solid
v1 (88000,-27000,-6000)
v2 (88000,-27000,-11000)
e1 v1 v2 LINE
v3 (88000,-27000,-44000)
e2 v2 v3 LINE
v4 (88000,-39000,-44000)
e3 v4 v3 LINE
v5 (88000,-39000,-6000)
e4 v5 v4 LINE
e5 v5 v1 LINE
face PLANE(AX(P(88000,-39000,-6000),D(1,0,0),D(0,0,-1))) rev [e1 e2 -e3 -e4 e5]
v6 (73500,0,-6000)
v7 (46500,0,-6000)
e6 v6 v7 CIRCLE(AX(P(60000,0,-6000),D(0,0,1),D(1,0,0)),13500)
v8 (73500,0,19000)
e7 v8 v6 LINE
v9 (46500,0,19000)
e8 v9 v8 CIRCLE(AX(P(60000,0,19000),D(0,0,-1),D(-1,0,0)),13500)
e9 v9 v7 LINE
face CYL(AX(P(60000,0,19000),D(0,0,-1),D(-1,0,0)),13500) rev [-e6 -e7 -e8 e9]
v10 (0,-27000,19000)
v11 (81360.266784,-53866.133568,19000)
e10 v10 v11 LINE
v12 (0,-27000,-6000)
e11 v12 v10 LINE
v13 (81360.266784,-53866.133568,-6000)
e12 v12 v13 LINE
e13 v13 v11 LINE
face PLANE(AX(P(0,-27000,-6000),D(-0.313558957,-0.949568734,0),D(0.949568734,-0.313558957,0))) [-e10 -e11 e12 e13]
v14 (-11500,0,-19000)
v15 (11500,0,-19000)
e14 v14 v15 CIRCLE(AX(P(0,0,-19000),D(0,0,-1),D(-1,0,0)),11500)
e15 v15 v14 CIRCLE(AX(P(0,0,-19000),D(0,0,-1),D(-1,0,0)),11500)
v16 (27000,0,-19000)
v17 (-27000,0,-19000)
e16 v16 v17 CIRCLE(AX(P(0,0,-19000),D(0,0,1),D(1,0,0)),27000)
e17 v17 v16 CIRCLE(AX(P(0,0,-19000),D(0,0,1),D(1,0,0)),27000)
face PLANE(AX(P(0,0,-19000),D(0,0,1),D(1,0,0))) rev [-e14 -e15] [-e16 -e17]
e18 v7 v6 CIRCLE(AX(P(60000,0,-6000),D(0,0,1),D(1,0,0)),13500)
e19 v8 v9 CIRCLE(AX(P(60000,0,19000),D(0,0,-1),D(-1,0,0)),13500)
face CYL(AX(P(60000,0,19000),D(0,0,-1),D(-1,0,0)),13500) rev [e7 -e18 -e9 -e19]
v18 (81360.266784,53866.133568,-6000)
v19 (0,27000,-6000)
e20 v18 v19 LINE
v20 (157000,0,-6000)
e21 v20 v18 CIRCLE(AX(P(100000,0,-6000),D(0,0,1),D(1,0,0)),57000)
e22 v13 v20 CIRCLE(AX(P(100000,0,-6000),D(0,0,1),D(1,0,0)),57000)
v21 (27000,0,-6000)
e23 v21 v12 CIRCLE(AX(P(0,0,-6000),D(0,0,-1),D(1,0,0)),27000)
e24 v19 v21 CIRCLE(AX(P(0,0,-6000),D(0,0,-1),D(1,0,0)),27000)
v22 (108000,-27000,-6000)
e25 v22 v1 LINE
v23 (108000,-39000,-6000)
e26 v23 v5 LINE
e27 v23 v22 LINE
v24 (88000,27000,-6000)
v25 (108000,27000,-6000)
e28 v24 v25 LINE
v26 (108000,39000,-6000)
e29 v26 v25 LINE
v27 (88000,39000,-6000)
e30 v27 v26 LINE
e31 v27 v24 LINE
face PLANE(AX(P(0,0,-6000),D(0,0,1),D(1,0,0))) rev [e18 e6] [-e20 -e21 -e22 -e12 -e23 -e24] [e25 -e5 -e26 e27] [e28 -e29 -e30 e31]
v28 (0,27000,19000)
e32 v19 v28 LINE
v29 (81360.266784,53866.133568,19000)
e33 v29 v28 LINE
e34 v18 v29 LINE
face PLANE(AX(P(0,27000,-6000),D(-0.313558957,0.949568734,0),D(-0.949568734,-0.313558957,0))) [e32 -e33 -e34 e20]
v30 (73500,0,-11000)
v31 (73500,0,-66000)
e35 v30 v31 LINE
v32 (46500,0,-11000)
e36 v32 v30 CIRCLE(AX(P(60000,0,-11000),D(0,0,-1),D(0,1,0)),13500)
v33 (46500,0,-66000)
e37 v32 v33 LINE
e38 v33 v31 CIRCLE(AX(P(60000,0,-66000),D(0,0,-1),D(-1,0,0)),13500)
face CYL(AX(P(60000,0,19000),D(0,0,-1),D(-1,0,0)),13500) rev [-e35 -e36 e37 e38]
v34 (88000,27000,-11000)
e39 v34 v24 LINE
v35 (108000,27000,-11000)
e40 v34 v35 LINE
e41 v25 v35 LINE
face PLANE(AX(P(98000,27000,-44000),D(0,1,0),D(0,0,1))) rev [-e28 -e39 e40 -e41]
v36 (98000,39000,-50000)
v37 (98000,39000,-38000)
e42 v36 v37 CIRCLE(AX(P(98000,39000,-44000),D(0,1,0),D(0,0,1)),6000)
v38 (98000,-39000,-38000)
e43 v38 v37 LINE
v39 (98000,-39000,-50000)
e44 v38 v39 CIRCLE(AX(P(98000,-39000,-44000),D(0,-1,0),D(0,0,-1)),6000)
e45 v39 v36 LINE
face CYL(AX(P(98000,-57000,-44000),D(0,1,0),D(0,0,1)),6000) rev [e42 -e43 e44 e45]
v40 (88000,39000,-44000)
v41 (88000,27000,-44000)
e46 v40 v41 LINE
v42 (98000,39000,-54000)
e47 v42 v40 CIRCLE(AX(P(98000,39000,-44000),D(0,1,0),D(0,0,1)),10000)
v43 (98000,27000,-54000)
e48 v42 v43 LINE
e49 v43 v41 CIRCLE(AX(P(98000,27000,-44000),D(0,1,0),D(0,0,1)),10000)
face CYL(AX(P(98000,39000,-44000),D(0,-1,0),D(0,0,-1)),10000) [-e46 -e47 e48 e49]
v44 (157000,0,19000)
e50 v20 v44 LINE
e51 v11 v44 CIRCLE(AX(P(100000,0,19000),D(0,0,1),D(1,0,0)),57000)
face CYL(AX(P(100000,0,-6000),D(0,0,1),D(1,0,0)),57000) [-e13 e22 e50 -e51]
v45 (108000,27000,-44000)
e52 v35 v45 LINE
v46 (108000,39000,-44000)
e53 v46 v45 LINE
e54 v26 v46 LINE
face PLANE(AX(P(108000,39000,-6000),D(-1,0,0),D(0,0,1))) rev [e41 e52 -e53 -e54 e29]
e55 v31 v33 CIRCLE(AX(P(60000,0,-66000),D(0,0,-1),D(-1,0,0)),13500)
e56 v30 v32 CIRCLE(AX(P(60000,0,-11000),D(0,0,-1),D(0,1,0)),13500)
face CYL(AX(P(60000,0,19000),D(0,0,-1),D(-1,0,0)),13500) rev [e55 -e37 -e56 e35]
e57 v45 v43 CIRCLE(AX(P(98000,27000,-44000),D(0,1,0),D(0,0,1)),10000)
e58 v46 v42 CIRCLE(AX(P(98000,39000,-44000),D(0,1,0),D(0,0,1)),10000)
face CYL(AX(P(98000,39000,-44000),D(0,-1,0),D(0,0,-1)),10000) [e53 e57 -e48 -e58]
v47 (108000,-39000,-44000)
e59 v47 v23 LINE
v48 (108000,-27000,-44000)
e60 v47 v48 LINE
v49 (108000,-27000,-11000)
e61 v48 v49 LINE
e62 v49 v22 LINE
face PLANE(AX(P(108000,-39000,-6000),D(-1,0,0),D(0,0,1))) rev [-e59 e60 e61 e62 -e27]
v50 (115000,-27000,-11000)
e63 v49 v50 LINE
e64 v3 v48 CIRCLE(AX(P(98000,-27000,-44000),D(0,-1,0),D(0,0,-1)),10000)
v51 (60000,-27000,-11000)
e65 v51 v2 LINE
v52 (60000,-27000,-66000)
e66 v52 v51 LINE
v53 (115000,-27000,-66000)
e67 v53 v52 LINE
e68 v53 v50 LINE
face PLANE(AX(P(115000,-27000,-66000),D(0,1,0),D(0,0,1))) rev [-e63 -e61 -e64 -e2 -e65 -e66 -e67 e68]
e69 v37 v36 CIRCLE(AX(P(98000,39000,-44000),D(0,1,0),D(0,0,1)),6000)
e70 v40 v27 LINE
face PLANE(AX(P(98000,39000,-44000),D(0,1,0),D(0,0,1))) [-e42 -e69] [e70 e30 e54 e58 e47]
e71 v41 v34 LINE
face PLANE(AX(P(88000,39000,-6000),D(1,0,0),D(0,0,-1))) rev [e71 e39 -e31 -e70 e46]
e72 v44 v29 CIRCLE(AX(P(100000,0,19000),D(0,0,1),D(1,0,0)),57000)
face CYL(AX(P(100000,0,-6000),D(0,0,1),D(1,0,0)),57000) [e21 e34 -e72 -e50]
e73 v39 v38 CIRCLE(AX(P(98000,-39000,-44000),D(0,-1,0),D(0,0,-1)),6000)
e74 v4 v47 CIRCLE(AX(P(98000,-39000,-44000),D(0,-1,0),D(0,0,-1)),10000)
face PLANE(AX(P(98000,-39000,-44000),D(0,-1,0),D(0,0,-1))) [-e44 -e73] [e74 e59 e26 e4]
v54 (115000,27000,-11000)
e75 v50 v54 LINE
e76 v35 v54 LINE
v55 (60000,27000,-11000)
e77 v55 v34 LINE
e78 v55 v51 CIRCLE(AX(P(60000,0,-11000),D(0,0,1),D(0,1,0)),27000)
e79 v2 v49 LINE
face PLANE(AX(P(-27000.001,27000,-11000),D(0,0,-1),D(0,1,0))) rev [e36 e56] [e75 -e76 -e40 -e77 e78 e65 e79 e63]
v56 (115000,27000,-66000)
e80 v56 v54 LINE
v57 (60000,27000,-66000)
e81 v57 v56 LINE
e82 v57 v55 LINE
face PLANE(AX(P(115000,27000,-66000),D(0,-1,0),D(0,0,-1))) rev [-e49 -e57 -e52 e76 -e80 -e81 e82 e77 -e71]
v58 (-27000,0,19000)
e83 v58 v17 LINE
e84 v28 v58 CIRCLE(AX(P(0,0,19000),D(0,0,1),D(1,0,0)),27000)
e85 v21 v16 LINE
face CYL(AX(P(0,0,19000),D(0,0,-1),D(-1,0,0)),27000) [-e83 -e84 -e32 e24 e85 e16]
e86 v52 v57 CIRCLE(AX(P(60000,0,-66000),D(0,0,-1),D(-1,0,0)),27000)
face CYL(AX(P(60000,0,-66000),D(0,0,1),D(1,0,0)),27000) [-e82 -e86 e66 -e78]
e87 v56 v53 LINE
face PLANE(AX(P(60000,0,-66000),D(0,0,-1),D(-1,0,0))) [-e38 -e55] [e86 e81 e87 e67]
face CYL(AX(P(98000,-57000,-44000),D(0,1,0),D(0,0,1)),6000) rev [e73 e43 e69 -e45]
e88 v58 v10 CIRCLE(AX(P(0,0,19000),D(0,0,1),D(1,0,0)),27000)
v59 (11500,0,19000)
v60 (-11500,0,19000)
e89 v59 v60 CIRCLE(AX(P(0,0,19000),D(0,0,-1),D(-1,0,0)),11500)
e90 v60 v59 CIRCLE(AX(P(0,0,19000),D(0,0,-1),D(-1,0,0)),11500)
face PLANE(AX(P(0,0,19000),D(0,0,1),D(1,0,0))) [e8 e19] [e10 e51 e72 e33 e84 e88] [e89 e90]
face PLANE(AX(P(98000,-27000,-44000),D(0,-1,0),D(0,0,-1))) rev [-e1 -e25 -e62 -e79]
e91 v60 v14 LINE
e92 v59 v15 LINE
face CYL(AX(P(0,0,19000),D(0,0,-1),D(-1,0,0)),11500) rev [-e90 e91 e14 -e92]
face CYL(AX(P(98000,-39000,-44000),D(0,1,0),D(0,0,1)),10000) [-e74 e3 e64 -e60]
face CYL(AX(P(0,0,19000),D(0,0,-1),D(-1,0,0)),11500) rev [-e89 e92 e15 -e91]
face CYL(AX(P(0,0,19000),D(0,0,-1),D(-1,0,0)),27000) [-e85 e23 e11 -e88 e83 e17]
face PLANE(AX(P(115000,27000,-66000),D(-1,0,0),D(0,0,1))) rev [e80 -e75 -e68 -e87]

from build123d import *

# Parameters (mm, degrees)
HUB_SKETCH_54_R      = 27000
HUB_BOSS_54_DEPTH    = 19000
BASE_PLATE_DEPTH     = 25000
MOUNTING_BLOCK_DEPTH = 60000
PLATE_HOLE_SKETCH_R  = 13500
PLATE_HOLE_DEPTH     = 187412.312358673
HUB_BORE_SKETCH_23_R = 11500
HUB_BORE_23_DEPTH    = 173514.688220843
BLOCK_SLOT_REACH     = 166642.331
BLOCK_SLOT_SKETCH_W  = 5000
BLOCK_SLOT_SKETCH_H  = 54000
CLEVIS_LUG_1_DEPTH   = 12000
CLEVIS_LUG_2_DEPTH   = 12000
PIN_HOLE_SKETCH_12_R = 6000
PIN_HOLE_12_DEPTH    = 195502.918149158


with BuildPart() as part:
    # Hub Sketch Ø54 → Hub Boss Ø54 (new, symmetric)
    with BuildSketch(Plane.XY):
        Circle(HUB_SKETCH_54_R)
    extrude(amount=HUB_BOSS_54_DEPTH, both=True)

    # Base Plate Sketch → Base Plate (add)
    with BuildSketch(Plane.XY.offset(19000)):
        with BuildLine():
            Line((0, 27000), (81360.266783536, 53866.133568496))
            ThreePointArc((81360.266783536, 53866.133568496), (157000, 0), (81360.266783536, -53866.133568496))
            Line((81360.266783536, -53866.133568496), (0, -27000))
            ThreePointArc((0, -27000), (27000, 0), (0, 27000))
        make_face()
    extrude(amount=-BASE_PLATE_DEPTH)

    # Mounting Block Sketch → Mounting Block (add)
    with BuildSketch(Plane(origin=(0, 0, -6000), x_dir=(-1, 0, 0), z_dir=(0, 0, -1))):
        with BuildLine():
            Line((-115000, 27000), (-60000, 27000))
            ThreePointArc((-60000, 27000), (-33000, 0), (-60000, -27000))
            Line((-60000, -27000), (-115000, -27000))
            Line((-115000, -27000), (-115000, 27000))
        make_face()
    extrude(amount=MOUNTING_BLOCK_DEPTH)

    # Plate Hole Sketch → Plate Hole (cut, through all)
    with BuildSketch(Plane(origin=(0, 0, -66000), x_dir=(-1, 0, 0), z_dir=(0, 0, -1))):
        with Locations((-60000, 0)):
            Circle(PLATE_HOLE_SKETCH_R)
    extrude(amount=-PLATE_HOLE_DEPTH, mode=Mode.SUBTRACT)

    # Hub Bore Sketch Ø23 → Hub Bore Ø23 (cut, through all)
    with BuildSketch(Plane(origin=(0, 0, -19000), x_dir=(-1, 0, 0), z_dir=(0, 0, -1))):
        Circle(HUB_BORE_SKETCH_23_R)
    extrude(amount=-HUB_BORE_23_DEPTH, mode=Mode.SUBTRACT)

    # Block Slot Sketch → Block Slot (cut, up to next)
    with BuildSketch(Plane(origin=(115000, 0, 0), x_dir=(0, 0, -1), z_dir=(1, 0, 0)), mode=Mode.PRIVATE) as block_slot_sk1:
        with Locations((8500, 0)):
            Rectangle(BLOCK_SLOT_SKETCH_W, BLOCK_SLOT_SKETCH_H)
    block_slot_tool1 = extrude(block_slot_sk1.sketch, amount=-BLOCK_SLOT_REACH, mode=Mode.PRIVATE) & part.part
    add(block_slot_tool1.solids().sort_by_distance((115000, 0, -8500))[0], mode=Mode.SUBTRACT)


with BuildPart() as block_slot_piece_1:
    # of the separate pieces the step leaves, piece 1, a body of its own (block_slot_pieces)
    add(part.part.solids().sort_by_distance((27000, 0, -19000))[0])



with BuildPart() as block_slot_piece_2:
    # of the separate pieces the step leaves, piece 2, a body of its own (block_slot_pieces)
    add(part.part.solids().sort_by_distance((60000, 27000, -11000))[0])


with BuildPart() as block_slot_piece_1_1:
    add(block_slot_piece_1.part)

    add(block_slot_piece_2.part)  # Clevis Lug 1 merges Block Slot piece 2
    # Clevis Lug 1 Sketch → Clevis Lug 1 (add)
    with BuildSketch(Plane.XZ.offset(27000)):
        with BuildLine():
            Line((108000, -6000), (88000, -6000))
            Line((88000, -6000), (88000, -44000))
            ThreePointArc((88000, -44000), (98000, -54000), (108000, -44000))
            Line((108000, -44000), (108000, -6000))
        make_face()
    extrude(amount=CLEVIS_LUG_1_DEPTH)

    # Clevis Lug 2 Sketch → Clevis Lug 2 (add)
    with BuildSketch(Plane(origin=(0, 27000, 0), x_dir=(1, 0, 0), z_dir=(0, 1, 0))):
        with BuildLine():
            Line((108000, 6000), (88000, 6000))
            Line((88000, 6000), (88000, 44000))
            ThreePointArc((88000, 44000), (98000, 54000), (108000, 44000))
            Line((108000, 44000), (108000, 6000))
        make_face()
    extrude(amount=CLEVIS_LUG_2_DEPTH)

    # Pin Hole Sketch Ø12 → Pin Hole Ø12 (cut, through all)
    with BuildSketch(Plane(origin=(0, 39000, 0), x_dir=(1, 0, 0), z_dir=(0, 1, 0))):
        with Locations(Location((98000, 44000, 0), (0, 0, 270))):
            Circle(PIN_HOLE_SKETCH_12_R)
    extrude(amount=-PIN_HOLE_12_DEPTH, mode=Mode.SUBTRACT)


solid = block_slot_piece_1_1.part
